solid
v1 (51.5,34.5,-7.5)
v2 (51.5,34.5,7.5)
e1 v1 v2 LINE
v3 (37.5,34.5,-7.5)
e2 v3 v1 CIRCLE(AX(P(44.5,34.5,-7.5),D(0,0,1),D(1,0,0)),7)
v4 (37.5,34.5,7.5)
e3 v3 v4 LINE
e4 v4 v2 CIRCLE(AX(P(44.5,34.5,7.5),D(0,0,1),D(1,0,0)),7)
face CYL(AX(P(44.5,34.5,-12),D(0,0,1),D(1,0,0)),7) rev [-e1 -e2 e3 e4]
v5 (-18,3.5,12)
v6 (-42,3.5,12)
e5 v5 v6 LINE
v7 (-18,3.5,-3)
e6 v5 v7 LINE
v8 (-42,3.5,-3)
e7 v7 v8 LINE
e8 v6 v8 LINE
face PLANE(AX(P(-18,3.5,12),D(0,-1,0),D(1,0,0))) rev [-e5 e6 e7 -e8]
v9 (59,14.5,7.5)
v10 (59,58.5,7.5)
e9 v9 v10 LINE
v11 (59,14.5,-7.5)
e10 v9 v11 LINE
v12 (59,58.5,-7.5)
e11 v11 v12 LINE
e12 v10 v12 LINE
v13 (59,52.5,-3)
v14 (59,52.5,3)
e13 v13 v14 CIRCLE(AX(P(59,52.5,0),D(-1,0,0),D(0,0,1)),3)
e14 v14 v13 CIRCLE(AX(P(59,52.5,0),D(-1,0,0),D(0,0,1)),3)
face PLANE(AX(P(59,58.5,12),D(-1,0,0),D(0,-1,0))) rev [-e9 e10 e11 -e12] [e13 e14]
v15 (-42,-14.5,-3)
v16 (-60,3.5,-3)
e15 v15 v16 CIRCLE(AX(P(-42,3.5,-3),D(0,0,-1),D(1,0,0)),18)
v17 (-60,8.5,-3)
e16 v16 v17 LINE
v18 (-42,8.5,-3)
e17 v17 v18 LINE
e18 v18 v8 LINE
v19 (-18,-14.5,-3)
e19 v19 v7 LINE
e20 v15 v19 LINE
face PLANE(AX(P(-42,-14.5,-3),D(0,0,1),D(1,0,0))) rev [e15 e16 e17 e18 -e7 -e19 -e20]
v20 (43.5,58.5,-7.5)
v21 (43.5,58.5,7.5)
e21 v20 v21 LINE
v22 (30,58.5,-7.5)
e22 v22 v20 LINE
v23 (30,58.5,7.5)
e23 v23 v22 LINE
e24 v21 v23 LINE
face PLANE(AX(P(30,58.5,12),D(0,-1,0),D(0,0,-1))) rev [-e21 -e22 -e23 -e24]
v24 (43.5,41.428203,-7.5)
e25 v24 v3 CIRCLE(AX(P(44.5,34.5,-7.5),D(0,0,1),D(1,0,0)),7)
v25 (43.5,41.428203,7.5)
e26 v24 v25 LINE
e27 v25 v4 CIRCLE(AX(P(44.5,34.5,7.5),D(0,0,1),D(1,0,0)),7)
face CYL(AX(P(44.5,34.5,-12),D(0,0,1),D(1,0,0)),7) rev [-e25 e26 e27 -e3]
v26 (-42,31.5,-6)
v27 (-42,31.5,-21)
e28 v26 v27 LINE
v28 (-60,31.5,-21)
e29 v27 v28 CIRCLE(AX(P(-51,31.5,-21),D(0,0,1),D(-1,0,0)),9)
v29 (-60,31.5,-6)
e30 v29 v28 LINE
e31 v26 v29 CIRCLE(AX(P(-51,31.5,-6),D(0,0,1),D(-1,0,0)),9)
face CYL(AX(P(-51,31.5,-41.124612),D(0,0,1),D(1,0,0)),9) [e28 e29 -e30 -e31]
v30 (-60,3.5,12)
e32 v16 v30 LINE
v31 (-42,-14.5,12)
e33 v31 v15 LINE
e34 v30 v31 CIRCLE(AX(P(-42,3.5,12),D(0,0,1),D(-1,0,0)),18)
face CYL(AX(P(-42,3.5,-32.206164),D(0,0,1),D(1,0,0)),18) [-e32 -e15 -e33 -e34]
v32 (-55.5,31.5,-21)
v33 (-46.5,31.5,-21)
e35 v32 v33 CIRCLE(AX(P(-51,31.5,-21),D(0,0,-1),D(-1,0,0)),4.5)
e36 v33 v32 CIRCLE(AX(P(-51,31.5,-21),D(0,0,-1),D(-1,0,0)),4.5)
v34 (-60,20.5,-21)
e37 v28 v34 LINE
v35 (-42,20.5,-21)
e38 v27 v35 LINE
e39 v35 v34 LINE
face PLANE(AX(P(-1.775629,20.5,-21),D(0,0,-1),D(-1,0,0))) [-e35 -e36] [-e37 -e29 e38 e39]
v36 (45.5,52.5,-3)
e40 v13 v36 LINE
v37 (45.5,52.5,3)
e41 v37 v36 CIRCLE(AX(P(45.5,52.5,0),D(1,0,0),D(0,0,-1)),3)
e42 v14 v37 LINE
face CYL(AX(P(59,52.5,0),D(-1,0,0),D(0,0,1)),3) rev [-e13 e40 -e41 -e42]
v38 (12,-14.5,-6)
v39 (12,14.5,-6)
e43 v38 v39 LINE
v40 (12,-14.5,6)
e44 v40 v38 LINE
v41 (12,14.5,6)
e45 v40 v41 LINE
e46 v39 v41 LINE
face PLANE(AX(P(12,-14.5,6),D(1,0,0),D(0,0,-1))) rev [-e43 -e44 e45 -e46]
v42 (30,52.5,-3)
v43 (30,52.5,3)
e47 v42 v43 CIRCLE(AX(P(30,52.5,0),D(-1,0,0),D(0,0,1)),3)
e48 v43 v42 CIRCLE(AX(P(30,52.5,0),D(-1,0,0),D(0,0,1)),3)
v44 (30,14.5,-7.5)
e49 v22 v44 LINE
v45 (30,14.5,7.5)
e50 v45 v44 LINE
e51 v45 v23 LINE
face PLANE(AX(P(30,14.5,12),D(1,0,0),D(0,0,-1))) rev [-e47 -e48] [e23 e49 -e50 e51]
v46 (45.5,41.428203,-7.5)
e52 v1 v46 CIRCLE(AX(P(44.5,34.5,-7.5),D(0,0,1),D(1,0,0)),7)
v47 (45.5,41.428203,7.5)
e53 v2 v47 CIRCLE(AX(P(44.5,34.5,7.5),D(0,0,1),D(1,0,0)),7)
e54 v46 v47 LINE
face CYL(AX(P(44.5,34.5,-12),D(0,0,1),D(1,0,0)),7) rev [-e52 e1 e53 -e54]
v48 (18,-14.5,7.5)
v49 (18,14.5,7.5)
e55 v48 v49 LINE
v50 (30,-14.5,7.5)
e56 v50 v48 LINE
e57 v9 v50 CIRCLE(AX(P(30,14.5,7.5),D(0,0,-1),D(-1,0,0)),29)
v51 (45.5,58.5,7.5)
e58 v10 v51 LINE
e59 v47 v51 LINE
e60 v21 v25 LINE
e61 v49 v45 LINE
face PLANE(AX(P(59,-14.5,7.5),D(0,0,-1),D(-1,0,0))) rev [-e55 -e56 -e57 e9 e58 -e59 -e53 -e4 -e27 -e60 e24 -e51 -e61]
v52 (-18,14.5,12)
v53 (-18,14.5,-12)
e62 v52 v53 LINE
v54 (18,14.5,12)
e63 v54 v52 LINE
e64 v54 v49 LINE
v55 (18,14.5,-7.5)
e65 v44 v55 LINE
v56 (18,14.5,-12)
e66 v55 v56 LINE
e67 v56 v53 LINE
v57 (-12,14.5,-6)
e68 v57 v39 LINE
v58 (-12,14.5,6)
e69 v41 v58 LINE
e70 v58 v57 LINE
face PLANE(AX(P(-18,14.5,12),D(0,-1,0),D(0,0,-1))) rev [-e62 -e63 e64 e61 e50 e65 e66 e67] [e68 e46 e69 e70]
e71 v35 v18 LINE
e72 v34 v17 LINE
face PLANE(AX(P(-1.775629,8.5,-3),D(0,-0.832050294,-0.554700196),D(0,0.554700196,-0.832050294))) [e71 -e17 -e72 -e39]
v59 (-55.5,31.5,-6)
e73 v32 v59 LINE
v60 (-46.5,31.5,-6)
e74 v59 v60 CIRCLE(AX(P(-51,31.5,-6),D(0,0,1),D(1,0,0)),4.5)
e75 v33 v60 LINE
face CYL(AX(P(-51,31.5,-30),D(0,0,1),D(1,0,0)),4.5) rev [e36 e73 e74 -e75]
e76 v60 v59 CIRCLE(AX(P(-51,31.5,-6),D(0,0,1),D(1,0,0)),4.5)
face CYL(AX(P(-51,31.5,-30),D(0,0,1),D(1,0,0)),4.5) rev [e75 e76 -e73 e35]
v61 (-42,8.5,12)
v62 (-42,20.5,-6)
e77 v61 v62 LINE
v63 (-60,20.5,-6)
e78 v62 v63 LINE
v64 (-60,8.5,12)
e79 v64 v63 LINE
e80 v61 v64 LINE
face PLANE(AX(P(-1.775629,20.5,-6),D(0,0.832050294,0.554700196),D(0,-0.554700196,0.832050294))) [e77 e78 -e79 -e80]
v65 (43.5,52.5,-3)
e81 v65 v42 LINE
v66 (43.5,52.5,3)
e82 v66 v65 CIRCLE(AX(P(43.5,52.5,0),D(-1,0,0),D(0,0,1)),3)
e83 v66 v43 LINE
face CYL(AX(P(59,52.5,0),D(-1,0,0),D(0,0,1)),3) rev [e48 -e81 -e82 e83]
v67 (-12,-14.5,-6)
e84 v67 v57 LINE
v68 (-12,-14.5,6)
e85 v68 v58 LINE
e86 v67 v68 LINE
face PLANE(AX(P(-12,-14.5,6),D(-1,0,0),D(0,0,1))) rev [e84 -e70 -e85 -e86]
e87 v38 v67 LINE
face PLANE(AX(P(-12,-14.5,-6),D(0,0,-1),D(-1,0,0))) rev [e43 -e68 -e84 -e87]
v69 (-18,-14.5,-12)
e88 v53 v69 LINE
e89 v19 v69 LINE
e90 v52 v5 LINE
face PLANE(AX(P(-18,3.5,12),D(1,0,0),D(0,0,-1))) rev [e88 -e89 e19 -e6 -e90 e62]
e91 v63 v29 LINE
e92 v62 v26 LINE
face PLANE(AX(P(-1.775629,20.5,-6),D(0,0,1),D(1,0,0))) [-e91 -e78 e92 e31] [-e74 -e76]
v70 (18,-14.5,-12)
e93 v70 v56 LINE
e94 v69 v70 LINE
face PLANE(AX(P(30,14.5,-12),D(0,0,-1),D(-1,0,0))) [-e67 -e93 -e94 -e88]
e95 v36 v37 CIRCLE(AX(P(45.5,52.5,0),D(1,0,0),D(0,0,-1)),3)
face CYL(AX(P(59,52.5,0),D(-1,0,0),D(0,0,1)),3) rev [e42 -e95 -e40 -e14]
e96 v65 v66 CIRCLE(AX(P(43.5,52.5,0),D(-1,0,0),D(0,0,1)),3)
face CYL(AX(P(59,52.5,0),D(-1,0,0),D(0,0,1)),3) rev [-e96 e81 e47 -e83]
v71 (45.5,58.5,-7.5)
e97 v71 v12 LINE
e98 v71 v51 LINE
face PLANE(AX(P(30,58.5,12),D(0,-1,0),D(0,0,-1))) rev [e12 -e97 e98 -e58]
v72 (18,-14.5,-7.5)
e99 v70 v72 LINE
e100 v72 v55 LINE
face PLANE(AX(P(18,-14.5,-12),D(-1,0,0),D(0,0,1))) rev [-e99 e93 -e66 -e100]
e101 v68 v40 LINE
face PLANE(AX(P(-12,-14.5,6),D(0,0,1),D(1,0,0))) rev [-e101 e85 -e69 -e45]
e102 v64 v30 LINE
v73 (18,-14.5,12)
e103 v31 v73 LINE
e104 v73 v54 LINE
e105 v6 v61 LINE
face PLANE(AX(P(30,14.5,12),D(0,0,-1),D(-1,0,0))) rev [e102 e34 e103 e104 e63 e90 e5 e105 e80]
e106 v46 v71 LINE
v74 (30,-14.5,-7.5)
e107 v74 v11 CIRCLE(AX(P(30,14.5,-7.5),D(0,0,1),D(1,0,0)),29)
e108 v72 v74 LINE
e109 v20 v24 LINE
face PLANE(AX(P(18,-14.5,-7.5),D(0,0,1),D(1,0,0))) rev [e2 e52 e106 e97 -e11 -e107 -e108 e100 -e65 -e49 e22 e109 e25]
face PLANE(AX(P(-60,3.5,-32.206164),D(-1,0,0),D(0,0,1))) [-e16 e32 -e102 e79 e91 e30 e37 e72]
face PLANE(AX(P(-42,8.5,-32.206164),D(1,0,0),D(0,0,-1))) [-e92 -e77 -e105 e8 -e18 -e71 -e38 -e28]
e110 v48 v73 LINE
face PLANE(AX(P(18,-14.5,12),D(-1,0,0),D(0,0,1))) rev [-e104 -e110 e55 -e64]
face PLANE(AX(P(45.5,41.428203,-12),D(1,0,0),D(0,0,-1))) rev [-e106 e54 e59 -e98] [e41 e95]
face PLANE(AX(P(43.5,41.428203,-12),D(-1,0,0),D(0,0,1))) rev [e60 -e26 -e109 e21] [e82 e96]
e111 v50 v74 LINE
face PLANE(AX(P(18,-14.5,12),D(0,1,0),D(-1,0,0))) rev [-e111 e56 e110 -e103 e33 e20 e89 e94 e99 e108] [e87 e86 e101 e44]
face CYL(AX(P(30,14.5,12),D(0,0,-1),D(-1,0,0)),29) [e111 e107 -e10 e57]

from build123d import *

# Parameters (mm, degrees)
BRACKET_BODY_DEPTH         = 12
BODY_RELIEF_CUT_DEPTH      = 75.57211275
BODY_RELIEF_CUT_DEPTH_BACK = 75.57211275
BODY_RELIEF_SKETCH_W       = 24
BODY_RELIEF_SKETCH_H       = 12
BODY_RELIEF_SKETCH_H_2     = 9
BODY_RELIEF_SKETCH_W_2     = 41
BODY_RELIEF_SKETCH_H_3     = 4.5
RECTANGULAR_WINDOW_DEPTH   = 86.343423883
CLAMP_HOLE_SKETCH_R        = 3
CLAMP_HOLE_6_DEPTH         = 94.542770966
ARM_BOSS_DEPTH             = 15
PIVOT_LUG_DEPTH            = 18
LUG_FILL_BOSS_DEPTH        = 15
PIVOT_BORE_SKETCH_R        = 4.5
PIVOT_BORE_9_DEPTH         = 24


with BuildPart() as part:
    # Bracket Profile Sketch → Bracket Body (new, symmetric)
    with BuildSketch(Plane.XY):
        with BuildLine():
            Line((30, 14.5), (30, 58.5))
            Line((30, 58.5), (59, 58.5))
            Line((59, 58.5), (59, 14.5))
            ThreePointArc((59, 14.5), (50.506096654, -6.006096654), (30, -14.5))
            Line((30, -14.5), (18, -14.5))
            Line((18, -14.5), (-18, -14.5))
            Line((-18, -14.5), (-42, -14.5))
            Line((-42, -14.5), (-42, 3.5))
            Line((-42, 3.5), (-18, 3.5))
            Line((-18, 3.5), (-18, 14.5))
            Line((-18, 14.5), (18, 14.5))
            Line((18, 14.5), (30, 14.5))
        make_face()
    extrude(amount=BRACKET_BODY_DEPTH, both=True)

    # Body Relief Sketch → Body Relief Cut (cut, two sides: drawn at the far end of the back side and taken through both)
    with BuildSketch(Plane(origin=(0, 14.5, 0), x_dir=(1, 0, 0), z_dir=(0, 1, 0)).offset(-BODY_RELIEF_CUT_DEPTH_BACK)):
        Rectangle(BODY_RELIEF_SKETCH_W, BODY_RELIEF_SKETCH_H)
        with Locations((-30, 7.5)):
            Rectangle(BODY_RELIEF_SKETCH_W, BODY_RELIEF_SKETCH_H_2)
        with Locations((38.5, -9.75)):
            Rectangle(BODY_RELIEF_SKETCH_W_2, BODY_RELIEF_SKETCH_H_3)
        with Locations((38.5, 9.75)):
            Rectangle(BODY_RELIEF_SKETCH_W_2, BODY_RELIEF_SKETCH_H_3)
    extrude(amount=BODY_RELIEF_CUT_DEPTH + BODY_RELIEF_CUT_DEPTH_BACK, mode=Mode.SUBTRACT)

    # Window Sketch → Rectangular Window (cut, through all)
    with BuildSketch(Plane.XY.offset(7.5)):
        with BuildLine():
            Line((43.5, 41.42820323), (43.5, 58.5))
            Line((43.5, 58.5), (45.5, 58.5))
            Line((45.5, 58.5), (45.5, 41.42820323))
            ThreePointArc((45.5, 41.42820323), (44.5, 27.5), (43.5, 41.42820323))
        make_face()
    extrude(amount=-RECTANGULAR_WINDOW_DEPTH, mode=Mode.SUBTRACT)

    # Clamp Hole Sketch → Clamp Hole Ø6 (cut, through all)
    with BuildSketch(Plane.ZY.offset(-30)):
        with Locations((0, 52.5)):
            Circle(CLAMP_HOLE_SKETCH_R)
    extrude(amount=-CLAMP_HOLE_6_DEPTH, mode=Mode.SUBTRACT)

    # Arm Sketch → Arm Boss (add)
    with BuildSketch(Plane.XY.offset(12)):
        with BuildLine():
            Line((-60, 3.5), (-60, 8.5))
            Line((-60, 8.5), (-42, 8.5))
            Line((-42, 8.5), (-42, 3.5))
            Line((-42, 3.5), (-42, -14.5))
            ThreePointArc((-42, -14.5), (-54.727922061, -9.227922061), (-60, 3.5))
        make_face()
    extrude(amount=-ARM_BOSS_DEPTH)

    # Pivot Lug Sketch → Pivot Lug (add)
    with BuildSketch(Plane.ZY.offset(60)):
        Polygon((-3, 8.5), (-21, 20.5), (-21, 31.5), (-6, 31.5), (-6, 20.5), (12, 8.5), align=None)
    extrude(amount=-PIVOT_LUG_DEPTH)

    # Lug Fill Sketch → Lug Fill Boss (add)
    with BuildSketch(Plane.XY.offset(-6)):
        with BuildLine():
            Line((-60, 31.5), (-42, 31.5))
            ThreePointArc((-42, 31.5), (-51, 40.5), (-60, 31.5))
        make_face()
    extrude(amount=-LUG_FILL_BOSS_DEPTH)

    # Pivot Bore Sketch → Pivot Bore Ø9 (cut)
    with BuildSketch(Plane.XY.offset(-6)):
        with Locations((-51, 31.5)):
            Circle(PIVOT_BORE_SKETCH_R)
    extrude(amount=-PIVOT_BORE_9_DEPTH, mode=Mode.SUBTRACT)


solid = part.part
